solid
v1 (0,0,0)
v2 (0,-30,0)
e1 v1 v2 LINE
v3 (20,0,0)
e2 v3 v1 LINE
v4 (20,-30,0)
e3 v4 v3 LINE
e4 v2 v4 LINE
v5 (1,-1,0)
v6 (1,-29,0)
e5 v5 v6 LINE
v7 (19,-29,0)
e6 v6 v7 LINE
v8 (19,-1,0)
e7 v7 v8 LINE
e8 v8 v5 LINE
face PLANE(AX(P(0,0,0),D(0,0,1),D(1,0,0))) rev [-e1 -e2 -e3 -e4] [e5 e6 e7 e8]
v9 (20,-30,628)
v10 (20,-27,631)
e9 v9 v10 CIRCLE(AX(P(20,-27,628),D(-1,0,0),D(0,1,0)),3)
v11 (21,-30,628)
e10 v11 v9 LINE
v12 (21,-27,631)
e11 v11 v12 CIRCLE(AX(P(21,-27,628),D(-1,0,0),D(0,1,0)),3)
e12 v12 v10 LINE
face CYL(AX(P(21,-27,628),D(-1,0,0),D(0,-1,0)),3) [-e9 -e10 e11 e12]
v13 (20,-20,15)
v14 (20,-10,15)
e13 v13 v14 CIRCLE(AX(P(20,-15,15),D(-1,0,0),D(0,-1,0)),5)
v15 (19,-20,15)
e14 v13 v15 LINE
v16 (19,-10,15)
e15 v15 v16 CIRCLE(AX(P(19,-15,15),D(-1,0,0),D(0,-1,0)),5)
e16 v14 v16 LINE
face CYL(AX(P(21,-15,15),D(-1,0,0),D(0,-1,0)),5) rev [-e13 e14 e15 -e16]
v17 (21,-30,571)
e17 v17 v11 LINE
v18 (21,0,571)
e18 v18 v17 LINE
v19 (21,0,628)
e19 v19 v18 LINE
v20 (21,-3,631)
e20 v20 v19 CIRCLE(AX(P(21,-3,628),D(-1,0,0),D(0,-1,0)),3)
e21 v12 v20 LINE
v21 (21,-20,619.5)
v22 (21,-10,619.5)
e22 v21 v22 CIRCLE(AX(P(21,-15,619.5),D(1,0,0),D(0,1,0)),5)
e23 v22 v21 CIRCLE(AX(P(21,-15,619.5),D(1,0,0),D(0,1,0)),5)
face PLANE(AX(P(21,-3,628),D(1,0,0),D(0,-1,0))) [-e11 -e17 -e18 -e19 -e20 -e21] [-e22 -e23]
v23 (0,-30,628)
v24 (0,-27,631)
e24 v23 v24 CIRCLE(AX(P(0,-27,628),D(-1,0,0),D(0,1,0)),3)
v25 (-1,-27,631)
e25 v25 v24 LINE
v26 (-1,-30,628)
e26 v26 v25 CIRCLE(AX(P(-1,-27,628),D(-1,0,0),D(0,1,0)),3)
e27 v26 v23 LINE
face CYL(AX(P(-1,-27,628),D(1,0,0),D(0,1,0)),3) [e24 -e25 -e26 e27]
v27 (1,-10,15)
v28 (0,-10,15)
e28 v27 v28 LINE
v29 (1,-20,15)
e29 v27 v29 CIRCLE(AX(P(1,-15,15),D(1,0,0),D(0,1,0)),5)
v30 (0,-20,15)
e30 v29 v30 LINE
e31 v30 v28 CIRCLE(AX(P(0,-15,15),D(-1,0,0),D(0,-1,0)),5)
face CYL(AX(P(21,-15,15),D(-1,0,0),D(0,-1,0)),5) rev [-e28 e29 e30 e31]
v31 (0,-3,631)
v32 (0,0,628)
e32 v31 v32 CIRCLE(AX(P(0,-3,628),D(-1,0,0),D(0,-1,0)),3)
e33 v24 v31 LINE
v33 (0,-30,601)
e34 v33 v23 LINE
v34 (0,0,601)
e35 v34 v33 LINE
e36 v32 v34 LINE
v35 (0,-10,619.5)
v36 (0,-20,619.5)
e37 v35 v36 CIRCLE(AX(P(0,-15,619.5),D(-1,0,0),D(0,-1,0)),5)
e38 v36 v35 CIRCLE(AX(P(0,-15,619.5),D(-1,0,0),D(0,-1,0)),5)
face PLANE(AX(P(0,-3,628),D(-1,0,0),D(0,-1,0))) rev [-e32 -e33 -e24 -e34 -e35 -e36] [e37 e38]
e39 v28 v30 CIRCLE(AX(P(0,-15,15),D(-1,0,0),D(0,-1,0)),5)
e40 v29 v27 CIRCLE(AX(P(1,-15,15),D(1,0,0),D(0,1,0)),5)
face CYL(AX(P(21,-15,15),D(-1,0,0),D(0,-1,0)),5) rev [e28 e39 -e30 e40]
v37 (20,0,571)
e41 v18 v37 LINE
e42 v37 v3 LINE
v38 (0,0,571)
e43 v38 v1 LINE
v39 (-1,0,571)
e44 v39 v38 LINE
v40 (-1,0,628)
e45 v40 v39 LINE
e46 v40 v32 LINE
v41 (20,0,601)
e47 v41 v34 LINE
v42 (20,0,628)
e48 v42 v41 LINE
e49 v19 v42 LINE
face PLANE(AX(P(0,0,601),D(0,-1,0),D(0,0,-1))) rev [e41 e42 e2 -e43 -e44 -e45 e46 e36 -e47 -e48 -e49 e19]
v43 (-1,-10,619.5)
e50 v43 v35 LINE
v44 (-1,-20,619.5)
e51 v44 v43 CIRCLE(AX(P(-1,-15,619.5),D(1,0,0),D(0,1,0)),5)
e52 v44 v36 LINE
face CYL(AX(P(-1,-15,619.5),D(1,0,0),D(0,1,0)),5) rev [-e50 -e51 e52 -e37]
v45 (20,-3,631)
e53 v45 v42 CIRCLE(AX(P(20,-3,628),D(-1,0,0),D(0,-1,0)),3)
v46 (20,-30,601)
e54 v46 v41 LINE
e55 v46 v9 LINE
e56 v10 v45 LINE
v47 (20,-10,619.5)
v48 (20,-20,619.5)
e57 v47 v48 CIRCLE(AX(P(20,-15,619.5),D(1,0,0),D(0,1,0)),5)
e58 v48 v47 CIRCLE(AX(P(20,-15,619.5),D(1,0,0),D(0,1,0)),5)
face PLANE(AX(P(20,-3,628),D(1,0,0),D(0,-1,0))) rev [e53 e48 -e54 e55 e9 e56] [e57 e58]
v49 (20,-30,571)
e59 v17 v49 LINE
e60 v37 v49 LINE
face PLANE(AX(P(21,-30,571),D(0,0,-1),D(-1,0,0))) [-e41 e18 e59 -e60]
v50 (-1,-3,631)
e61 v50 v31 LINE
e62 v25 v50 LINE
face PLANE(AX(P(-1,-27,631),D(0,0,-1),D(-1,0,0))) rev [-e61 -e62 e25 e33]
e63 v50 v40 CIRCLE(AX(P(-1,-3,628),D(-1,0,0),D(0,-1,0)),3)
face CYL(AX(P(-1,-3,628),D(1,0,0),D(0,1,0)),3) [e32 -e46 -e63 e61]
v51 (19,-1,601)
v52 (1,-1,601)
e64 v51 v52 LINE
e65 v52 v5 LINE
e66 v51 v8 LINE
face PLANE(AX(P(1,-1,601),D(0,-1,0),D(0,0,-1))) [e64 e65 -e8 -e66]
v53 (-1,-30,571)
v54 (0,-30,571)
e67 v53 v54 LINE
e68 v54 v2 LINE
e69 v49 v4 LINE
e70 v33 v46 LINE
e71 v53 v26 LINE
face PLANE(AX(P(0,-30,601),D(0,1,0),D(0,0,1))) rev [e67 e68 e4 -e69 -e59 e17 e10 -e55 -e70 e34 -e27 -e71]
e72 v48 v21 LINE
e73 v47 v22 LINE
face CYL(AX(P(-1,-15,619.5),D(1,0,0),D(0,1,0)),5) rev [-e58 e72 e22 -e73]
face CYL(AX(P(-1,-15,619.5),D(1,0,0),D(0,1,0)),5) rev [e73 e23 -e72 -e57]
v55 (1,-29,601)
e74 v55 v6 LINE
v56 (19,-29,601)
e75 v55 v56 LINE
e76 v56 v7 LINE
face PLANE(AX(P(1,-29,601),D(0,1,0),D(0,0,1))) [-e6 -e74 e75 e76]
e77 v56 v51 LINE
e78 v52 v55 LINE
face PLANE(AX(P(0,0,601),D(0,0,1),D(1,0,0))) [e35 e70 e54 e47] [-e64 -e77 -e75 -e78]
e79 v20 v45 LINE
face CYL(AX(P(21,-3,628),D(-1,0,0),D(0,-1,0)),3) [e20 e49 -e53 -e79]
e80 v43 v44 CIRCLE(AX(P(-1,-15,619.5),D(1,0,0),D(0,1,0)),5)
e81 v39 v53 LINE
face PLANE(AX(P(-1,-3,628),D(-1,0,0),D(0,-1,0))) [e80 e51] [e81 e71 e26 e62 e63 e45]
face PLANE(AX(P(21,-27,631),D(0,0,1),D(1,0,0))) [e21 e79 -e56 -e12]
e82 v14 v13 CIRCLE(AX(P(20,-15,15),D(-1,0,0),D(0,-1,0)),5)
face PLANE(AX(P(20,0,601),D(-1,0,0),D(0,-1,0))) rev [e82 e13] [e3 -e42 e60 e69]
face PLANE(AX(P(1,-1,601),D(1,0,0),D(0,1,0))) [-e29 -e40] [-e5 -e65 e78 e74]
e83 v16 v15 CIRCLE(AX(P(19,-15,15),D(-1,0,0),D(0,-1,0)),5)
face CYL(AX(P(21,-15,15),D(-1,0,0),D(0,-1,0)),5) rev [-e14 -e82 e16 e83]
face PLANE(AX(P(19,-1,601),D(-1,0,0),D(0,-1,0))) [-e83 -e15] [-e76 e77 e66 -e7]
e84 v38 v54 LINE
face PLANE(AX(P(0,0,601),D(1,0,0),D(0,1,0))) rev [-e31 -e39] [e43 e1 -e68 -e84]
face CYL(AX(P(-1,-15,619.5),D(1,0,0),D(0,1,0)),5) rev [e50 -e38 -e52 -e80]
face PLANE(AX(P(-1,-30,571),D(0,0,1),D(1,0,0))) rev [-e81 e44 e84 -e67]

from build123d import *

# Parameters (mm, degrees)
SKETCH1_W           = 20
SKETCH1_H           = 30
SKETCH1_W_2         = 18
SKETCH1_H_2         = 28
BOSS_EXTRUDE1_DEPTH = 601
BOSS_EXTRUDE2_DEPTH = 1
SKETCH4_R           = 5
CUT_EXTRUDE1_DEPTH  = 633.095720599
SKETCH5_R           = 5
CUT_EXTRUDE2_DEPTH  = 633.061705848


with BuildPart() as part:
    # Sketch1 → Boss-Extrude1 (new body)
    with BuildSketch(Plane.XY):
        with Locations((10, -15)):
            Rectangle(SKETCH1_W, SKETCH1_H)
        with Locations((10, -15)):
            Rectangle(SKETCH1_W_2, SKETCH1_H_2, mode=Mode.SUBTRACT)
    extrude(amount=BOSS_EXTRUDE1_DEPTH)

    # Sketch3 → Boss-Extrude2 (add)
    with BuildSketch(Plane.ZY):
        with BuildLine():
            Line((571, -30), (601, -30))
            Line((601, -30), (628, -30))
            ThreePointArc((628, -30), (630.121320344, -29.121320344), (631, -27))
            Line((631, -27), (631, -3))
            ThreePointArc((631, -3), (630.121320344, -0.878679656), (628, 0))
            Line((628, 0), (601, 0))
            Line((601, 0), (571, 0))
            Line((571, 0), (571, -30))
        make_face()
    boss_extrude2 = extrude(amount=BOSS_EXTRUDE2_DEPTH)

    # Mirror2: Boss-Extrude2 across plane
    add(boss_extrude2.mirror(Plane(origin=(10, 0, 0), x_dir=(0, 0, 1), z_dir=(1, 0, 0))))

    # Sketch4 → Cut-Extrude1 (cut, through all)
    with BuildSketch(Plane(origin=(21, 0, 0), x_dir=(0, 0, -1), z_dir=(1, 0, 0))):
        with Locations(Location((-619.5, -15, 0), (0, 0, 90))):
            Circle(SKETCH4_R)
    extrude(amount=-CUT_EXTRUDE1_DEPTH, mode=Mode.SUBTRACT)

    # Sketch5 → Cut-Extrude2 (cut, through all)
    with BuildSketch(Plane.ZY):
        with Locations(Location((15, -15, 0), (0, 0, 270))):
            Circle(SKETCH5_R)
    extrude(amount=-CUT_EXTRUDE2_DEPTH, mode=Mode.SUBTRACT)


solid = part.part
